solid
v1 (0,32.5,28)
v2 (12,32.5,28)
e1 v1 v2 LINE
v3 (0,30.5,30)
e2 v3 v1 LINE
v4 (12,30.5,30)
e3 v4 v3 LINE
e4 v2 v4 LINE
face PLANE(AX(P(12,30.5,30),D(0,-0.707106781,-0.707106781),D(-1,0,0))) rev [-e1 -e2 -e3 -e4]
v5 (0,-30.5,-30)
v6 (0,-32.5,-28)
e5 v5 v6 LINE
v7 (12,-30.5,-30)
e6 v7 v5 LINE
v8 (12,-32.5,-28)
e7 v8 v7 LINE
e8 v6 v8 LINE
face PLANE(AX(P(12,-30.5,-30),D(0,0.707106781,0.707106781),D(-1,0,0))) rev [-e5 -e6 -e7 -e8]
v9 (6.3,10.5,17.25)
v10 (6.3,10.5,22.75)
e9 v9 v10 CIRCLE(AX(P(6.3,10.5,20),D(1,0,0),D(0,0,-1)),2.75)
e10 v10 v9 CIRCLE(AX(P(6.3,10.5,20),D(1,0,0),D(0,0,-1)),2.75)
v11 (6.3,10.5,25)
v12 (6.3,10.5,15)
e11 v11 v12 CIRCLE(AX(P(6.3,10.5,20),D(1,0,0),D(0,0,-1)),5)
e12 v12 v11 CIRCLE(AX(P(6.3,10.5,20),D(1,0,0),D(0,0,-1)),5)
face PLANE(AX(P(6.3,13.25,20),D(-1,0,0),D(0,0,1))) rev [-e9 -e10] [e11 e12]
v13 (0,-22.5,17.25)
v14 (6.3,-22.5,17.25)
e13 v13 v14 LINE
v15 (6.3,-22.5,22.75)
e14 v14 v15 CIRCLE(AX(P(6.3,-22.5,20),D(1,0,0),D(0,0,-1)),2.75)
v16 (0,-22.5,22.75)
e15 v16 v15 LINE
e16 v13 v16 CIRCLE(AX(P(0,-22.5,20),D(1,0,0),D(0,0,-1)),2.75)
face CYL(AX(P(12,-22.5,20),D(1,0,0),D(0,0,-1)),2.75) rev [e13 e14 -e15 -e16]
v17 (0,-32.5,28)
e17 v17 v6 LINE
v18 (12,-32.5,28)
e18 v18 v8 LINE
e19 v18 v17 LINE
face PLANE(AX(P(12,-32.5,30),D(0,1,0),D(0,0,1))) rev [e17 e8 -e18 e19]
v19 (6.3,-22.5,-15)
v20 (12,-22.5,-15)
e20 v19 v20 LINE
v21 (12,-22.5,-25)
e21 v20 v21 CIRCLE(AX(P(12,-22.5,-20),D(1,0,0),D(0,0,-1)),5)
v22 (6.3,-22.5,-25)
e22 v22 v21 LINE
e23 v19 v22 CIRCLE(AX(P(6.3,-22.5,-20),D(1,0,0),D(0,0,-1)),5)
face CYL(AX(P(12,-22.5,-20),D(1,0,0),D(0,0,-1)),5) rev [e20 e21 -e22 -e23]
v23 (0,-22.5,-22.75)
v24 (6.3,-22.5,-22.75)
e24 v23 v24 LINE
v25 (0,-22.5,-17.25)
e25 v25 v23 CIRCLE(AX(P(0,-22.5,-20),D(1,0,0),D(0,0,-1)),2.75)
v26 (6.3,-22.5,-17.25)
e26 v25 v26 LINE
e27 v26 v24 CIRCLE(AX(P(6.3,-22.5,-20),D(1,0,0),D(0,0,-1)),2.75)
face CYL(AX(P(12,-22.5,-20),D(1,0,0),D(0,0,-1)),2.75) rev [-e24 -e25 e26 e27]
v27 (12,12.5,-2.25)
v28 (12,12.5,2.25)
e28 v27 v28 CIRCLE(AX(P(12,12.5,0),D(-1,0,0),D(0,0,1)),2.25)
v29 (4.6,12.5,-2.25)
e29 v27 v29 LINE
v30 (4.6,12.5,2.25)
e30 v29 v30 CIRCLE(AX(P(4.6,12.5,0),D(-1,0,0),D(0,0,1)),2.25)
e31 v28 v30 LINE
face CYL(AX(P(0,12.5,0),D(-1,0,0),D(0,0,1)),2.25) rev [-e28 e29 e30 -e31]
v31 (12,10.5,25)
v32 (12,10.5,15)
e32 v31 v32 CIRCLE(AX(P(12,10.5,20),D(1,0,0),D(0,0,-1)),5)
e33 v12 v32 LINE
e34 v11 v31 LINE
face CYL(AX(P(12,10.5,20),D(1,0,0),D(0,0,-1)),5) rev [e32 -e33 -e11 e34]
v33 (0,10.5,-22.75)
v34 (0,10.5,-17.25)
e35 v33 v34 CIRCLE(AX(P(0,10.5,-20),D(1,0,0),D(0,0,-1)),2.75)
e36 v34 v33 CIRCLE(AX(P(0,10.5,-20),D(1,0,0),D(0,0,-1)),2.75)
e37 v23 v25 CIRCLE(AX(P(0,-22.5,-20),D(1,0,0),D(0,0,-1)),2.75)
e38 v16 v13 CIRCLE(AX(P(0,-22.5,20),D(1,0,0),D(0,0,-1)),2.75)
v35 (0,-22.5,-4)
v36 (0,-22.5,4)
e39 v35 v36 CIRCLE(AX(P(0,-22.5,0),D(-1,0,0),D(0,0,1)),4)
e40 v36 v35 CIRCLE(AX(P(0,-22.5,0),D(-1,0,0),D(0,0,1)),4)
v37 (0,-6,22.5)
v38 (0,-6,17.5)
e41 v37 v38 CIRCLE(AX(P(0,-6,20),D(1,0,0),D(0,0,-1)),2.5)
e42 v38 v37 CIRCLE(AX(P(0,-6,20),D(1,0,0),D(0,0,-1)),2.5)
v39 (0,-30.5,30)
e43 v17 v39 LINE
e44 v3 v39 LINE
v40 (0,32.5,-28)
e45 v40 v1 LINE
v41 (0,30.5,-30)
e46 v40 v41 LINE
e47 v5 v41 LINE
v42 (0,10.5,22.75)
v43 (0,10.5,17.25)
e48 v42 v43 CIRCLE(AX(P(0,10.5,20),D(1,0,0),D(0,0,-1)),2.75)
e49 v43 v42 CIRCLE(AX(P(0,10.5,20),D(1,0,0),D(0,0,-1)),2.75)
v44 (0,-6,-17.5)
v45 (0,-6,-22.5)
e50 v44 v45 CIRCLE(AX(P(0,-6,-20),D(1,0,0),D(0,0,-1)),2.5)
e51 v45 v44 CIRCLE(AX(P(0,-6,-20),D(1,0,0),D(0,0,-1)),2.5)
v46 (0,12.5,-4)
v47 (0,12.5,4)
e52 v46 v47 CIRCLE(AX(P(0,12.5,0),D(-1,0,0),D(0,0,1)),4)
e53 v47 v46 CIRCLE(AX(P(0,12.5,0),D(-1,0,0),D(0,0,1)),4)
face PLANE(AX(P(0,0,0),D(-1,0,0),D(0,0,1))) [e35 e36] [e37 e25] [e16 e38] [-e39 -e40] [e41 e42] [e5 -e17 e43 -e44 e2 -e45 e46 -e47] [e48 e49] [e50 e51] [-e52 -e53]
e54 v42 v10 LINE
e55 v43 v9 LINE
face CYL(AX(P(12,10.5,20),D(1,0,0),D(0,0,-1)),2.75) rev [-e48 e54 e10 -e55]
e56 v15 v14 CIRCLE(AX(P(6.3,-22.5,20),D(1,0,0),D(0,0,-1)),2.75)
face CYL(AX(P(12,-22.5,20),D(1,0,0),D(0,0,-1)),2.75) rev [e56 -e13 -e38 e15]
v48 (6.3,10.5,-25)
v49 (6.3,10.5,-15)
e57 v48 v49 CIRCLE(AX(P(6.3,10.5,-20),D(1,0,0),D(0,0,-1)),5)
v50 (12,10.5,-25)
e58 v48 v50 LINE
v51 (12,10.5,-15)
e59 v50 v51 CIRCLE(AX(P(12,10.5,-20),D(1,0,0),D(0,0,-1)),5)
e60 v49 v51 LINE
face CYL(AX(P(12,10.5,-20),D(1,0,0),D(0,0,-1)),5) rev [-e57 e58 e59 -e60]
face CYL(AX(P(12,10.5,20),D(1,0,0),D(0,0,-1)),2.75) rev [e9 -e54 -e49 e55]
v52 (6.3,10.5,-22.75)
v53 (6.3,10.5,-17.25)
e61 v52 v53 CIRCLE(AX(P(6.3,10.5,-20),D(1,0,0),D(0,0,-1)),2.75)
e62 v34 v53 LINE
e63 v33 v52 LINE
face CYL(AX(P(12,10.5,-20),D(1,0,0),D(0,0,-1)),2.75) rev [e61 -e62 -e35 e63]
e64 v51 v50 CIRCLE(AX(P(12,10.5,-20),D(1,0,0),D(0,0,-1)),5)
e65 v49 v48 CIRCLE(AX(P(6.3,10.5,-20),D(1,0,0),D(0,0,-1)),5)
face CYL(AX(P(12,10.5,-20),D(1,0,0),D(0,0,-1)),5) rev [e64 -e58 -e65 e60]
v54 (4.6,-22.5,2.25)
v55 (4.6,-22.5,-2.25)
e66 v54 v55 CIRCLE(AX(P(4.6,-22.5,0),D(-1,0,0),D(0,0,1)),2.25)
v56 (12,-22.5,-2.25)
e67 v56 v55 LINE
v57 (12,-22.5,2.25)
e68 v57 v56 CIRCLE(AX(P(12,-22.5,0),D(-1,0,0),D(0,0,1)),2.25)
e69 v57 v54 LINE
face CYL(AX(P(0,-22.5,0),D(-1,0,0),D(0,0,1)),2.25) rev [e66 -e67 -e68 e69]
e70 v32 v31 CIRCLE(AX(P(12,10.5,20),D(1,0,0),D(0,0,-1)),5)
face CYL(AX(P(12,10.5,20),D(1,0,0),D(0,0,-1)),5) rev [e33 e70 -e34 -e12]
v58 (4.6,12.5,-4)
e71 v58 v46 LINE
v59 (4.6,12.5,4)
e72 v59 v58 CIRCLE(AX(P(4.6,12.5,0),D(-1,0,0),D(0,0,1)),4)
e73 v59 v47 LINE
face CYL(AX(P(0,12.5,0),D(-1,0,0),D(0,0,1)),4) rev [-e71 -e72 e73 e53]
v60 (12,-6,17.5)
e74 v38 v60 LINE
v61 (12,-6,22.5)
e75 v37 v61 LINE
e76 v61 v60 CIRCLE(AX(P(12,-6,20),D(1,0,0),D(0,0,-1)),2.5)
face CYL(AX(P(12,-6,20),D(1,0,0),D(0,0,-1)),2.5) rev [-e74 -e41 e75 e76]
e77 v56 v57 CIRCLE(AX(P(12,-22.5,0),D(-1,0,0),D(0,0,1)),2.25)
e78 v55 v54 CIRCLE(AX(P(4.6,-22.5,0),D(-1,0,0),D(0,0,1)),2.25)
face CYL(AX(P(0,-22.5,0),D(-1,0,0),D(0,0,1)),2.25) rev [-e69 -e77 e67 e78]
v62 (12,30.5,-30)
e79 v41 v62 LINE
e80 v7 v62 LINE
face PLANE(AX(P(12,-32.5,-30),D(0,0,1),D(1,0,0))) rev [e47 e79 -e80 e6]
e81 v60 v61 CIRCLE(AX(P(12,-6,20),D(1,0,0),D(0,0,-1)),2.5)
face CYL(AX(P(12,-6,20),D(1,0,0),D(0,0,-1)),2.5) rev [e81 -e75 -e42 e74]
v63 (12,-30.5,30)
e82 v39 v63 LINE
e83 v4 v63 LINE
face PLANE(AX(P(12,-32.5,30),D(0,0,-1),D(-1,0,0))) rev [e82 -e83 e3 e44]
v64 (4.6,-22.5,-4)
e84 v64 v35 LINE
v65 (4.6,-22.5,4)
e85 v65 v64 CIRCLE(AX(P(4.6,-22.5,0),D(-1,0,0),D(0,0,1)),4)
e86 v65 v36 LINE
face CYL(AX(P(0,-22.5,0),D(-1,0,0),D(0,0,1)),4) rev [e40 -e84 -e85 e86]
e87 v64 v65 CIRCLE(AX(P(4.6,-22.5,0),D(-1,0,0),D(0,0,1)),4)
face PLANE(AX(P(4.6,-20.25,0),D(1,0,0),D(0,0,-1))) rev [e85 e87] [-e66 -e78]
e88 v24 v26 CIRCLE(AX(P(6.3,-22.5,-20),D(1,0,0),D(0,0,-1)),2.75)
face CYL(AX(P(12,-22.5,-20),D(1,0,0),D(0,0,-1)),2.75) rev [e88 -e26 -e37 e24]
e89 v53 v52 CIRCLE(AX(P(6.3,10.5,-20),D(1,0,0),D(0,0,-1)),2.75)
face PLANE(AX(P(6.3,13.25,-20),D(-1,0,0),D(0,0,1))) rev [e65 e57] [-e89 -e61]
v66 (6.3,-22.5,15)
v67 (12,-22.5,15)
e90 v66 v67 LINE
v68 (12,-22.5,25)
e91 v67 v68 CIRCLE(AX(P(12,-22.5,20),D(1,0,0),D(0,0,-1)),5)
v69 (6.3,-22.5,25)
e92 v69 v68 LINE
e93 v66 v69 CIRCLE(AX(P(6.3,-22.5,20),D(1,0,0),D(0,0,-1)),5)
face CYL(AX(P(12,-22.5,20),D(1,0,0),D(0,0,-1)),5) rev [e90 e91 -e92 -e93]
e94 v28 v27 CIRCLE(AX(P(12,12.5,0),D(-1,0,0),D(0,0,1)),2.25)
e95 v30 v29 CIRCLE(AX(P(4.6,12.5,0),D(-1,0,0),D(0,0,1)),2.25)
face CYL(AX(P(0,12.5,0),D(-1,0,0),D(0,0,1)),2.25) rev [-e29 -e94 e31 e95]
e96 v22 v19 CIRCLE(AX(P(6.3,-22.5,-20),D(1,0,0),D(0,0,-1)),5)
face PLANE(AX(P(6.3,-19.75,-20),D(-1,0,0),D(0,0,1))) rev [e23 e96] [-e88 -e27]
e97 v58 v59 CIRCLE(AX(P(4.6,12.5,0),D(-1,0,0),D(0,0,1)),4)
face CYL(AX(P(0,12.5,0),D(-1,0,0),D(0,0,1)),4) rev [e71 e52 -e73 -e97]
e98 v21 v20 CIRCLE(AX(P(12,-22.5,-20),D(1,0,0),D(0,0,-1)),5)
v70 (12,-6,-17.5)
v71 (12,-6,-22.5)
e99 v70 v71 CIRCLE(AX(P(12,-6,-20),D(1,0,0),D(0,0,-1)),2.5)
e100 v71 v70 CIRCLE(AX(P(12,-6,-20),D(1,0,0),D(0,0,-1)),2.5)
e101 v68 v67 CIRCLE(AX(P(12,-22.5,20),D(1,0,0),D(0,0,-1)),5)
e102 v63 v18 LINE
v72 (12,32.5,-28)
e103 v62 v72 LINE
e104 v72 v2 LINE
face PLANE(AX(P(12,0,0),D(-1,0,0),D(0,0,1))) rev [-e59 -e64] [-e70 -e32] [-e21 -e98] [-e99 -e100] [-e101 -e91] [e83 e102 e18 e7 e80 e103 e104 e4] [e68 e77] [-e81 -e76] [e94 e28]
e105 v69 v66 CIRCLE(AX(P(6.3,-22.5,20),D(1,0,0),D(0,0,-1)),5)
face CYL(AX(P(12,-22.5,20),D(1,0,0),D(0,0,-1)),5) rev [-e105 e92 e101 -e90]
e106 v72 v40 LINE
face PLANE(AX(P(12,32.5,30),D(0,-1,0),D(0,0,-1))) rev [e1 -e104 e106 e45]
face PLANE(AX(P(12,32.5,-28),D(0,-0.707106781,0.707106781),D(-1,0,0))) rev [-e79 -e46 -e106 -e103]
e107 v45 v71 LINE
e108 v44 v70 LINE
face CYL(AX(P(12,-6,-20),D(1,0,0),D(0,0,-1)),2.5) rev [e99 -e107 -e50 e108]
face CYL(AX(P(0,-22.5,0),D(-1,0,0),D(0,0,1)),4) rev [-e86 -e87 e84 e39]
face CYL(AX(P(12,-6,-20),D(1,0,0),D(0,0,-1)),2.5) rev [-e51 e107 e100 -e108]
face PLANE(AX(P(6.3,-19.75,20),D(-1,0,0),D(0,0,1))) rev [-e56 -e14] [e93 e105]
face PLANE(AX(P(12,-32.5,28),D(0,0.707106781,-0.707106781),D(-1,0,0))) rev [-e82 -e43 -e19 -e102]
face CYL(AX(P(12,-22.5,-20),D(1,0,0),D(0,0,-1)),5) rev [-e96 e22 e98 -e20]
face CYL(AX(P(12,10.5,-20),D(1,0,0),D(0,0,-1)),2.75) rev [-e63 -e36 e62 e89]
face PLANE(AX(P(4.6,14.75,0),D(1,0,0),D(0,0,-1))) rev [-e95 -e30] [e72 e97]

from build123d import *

# Parameters (mm, degrees)
SKETCH1_W                                            = 60
SKETCH1_H                                            = 65
BOSS_EXTRUDE1_DEPTH                                  = 12
CBORE_FOR_M4_HEXAGON_SOCKET_HEAD_CAP_SCR_D           = 4.5
CBORE_FOR_M4_HEXAGON_SOCKET_HEAD_CAP_SCR_CBORE_D     = 8
CBORE_FOR_M4_HEXAGON_SOCKET_HEAD_CAP_SCR_CBORE_DEPTH = 4.6
CBORE_FOR_M5_HEXAGON_SOCKET_HEAD_CAP_SCR_D           = 5.5
CBORE_FOR_M5_HEXAGON_SOCKET_HEAD_CAP_SCR_CBORE_D     = 10
CBORE_FOR_M5_HEXAGON_SOCKET_HEAD_CAP_SCR_CBORE_DEPTH = 5.7
CHAMFER1_SIZE                                        = 2
F_5_0MM_BLIND_DOWEL_HOLE1_D                          = 5


with BuildPart() as part:
    # Sketch1 → Boss-Extrude1 (new body)
    with BuildSketch(Plane(origin=(0, 0, 0), x_dir=(0, 0, -1), z_dir=(1, 0, 0))):
        Rectangle(SKETCH1_W, SKETCH1_H)
    extrude(amount=BOSS_EXTRUDE1_DEPTH)

    # CBORE for M4 Hexagon socket head cap screws1 (through all)
    with Locations(Plane.ZY):
        with Locations((0, 12.5), (0, -22.5)):
            CounterBoreHole(CBORE_FOR_M4_HEXAGON_SOCKET_HEAD_CAP_SCR_D / 2, CBORE_FOR_M4_HEXAGON_SOCKET_HEAD_CAP_SCR_CBORE_D / 2, CBORE_FOR_M4_HEXAGON_SOCKET_HEAD_CAP_SCR_CBORE_DEPTH)

    # CBORE for M5 Hexagon socket head cap screws1 (through all)
    with Locations(Plane(origin=(12, 0, 0), x_dir=(0, 0, -1), z_dir=(1, 0, 0))):
        with Locations((-20, 10.5), (-20, -22.5), (20, -22.5), (20, 10.5)):
            CounterBoreHole(CBORE_FOR_M5_HEXAGON_SOCKET_HEAD_CAP_SCR_D / 2, CBORE_FOR_M5_HEXAGON_SOCKET_HEAD_CAP_SCR_CBORE_D / 2, CBORE_FOR_M5_HEXAGON_SOCKET_HEAD_CAP_SCR_CBORE_DEPTH)

    # Chamfer1
    chamfer1_edges = [part.edges().sort_by_distance(p)[0] for p in [
        (6, -32.5, -30),
        (6, -32.5, 30),
        (6, 32.5, 30),
        (6, 32.5, -30),
    ]]
    chamfer(chamfer1_edges, length=CHAMFER1_SIZE)

    # Ø5.0mm blind dowel hole1 (through all)
    with Locations(Plane(origin=(12, 0, 0), x_dir=(0, 0, -1), z_dir=(1, 0, 0))):
        with Locations((-20, -6), (20, -6)):
            Hole(F_5_0MM_BLIND_DOWEL_HOLE1_D / 2)


solid = part.part
